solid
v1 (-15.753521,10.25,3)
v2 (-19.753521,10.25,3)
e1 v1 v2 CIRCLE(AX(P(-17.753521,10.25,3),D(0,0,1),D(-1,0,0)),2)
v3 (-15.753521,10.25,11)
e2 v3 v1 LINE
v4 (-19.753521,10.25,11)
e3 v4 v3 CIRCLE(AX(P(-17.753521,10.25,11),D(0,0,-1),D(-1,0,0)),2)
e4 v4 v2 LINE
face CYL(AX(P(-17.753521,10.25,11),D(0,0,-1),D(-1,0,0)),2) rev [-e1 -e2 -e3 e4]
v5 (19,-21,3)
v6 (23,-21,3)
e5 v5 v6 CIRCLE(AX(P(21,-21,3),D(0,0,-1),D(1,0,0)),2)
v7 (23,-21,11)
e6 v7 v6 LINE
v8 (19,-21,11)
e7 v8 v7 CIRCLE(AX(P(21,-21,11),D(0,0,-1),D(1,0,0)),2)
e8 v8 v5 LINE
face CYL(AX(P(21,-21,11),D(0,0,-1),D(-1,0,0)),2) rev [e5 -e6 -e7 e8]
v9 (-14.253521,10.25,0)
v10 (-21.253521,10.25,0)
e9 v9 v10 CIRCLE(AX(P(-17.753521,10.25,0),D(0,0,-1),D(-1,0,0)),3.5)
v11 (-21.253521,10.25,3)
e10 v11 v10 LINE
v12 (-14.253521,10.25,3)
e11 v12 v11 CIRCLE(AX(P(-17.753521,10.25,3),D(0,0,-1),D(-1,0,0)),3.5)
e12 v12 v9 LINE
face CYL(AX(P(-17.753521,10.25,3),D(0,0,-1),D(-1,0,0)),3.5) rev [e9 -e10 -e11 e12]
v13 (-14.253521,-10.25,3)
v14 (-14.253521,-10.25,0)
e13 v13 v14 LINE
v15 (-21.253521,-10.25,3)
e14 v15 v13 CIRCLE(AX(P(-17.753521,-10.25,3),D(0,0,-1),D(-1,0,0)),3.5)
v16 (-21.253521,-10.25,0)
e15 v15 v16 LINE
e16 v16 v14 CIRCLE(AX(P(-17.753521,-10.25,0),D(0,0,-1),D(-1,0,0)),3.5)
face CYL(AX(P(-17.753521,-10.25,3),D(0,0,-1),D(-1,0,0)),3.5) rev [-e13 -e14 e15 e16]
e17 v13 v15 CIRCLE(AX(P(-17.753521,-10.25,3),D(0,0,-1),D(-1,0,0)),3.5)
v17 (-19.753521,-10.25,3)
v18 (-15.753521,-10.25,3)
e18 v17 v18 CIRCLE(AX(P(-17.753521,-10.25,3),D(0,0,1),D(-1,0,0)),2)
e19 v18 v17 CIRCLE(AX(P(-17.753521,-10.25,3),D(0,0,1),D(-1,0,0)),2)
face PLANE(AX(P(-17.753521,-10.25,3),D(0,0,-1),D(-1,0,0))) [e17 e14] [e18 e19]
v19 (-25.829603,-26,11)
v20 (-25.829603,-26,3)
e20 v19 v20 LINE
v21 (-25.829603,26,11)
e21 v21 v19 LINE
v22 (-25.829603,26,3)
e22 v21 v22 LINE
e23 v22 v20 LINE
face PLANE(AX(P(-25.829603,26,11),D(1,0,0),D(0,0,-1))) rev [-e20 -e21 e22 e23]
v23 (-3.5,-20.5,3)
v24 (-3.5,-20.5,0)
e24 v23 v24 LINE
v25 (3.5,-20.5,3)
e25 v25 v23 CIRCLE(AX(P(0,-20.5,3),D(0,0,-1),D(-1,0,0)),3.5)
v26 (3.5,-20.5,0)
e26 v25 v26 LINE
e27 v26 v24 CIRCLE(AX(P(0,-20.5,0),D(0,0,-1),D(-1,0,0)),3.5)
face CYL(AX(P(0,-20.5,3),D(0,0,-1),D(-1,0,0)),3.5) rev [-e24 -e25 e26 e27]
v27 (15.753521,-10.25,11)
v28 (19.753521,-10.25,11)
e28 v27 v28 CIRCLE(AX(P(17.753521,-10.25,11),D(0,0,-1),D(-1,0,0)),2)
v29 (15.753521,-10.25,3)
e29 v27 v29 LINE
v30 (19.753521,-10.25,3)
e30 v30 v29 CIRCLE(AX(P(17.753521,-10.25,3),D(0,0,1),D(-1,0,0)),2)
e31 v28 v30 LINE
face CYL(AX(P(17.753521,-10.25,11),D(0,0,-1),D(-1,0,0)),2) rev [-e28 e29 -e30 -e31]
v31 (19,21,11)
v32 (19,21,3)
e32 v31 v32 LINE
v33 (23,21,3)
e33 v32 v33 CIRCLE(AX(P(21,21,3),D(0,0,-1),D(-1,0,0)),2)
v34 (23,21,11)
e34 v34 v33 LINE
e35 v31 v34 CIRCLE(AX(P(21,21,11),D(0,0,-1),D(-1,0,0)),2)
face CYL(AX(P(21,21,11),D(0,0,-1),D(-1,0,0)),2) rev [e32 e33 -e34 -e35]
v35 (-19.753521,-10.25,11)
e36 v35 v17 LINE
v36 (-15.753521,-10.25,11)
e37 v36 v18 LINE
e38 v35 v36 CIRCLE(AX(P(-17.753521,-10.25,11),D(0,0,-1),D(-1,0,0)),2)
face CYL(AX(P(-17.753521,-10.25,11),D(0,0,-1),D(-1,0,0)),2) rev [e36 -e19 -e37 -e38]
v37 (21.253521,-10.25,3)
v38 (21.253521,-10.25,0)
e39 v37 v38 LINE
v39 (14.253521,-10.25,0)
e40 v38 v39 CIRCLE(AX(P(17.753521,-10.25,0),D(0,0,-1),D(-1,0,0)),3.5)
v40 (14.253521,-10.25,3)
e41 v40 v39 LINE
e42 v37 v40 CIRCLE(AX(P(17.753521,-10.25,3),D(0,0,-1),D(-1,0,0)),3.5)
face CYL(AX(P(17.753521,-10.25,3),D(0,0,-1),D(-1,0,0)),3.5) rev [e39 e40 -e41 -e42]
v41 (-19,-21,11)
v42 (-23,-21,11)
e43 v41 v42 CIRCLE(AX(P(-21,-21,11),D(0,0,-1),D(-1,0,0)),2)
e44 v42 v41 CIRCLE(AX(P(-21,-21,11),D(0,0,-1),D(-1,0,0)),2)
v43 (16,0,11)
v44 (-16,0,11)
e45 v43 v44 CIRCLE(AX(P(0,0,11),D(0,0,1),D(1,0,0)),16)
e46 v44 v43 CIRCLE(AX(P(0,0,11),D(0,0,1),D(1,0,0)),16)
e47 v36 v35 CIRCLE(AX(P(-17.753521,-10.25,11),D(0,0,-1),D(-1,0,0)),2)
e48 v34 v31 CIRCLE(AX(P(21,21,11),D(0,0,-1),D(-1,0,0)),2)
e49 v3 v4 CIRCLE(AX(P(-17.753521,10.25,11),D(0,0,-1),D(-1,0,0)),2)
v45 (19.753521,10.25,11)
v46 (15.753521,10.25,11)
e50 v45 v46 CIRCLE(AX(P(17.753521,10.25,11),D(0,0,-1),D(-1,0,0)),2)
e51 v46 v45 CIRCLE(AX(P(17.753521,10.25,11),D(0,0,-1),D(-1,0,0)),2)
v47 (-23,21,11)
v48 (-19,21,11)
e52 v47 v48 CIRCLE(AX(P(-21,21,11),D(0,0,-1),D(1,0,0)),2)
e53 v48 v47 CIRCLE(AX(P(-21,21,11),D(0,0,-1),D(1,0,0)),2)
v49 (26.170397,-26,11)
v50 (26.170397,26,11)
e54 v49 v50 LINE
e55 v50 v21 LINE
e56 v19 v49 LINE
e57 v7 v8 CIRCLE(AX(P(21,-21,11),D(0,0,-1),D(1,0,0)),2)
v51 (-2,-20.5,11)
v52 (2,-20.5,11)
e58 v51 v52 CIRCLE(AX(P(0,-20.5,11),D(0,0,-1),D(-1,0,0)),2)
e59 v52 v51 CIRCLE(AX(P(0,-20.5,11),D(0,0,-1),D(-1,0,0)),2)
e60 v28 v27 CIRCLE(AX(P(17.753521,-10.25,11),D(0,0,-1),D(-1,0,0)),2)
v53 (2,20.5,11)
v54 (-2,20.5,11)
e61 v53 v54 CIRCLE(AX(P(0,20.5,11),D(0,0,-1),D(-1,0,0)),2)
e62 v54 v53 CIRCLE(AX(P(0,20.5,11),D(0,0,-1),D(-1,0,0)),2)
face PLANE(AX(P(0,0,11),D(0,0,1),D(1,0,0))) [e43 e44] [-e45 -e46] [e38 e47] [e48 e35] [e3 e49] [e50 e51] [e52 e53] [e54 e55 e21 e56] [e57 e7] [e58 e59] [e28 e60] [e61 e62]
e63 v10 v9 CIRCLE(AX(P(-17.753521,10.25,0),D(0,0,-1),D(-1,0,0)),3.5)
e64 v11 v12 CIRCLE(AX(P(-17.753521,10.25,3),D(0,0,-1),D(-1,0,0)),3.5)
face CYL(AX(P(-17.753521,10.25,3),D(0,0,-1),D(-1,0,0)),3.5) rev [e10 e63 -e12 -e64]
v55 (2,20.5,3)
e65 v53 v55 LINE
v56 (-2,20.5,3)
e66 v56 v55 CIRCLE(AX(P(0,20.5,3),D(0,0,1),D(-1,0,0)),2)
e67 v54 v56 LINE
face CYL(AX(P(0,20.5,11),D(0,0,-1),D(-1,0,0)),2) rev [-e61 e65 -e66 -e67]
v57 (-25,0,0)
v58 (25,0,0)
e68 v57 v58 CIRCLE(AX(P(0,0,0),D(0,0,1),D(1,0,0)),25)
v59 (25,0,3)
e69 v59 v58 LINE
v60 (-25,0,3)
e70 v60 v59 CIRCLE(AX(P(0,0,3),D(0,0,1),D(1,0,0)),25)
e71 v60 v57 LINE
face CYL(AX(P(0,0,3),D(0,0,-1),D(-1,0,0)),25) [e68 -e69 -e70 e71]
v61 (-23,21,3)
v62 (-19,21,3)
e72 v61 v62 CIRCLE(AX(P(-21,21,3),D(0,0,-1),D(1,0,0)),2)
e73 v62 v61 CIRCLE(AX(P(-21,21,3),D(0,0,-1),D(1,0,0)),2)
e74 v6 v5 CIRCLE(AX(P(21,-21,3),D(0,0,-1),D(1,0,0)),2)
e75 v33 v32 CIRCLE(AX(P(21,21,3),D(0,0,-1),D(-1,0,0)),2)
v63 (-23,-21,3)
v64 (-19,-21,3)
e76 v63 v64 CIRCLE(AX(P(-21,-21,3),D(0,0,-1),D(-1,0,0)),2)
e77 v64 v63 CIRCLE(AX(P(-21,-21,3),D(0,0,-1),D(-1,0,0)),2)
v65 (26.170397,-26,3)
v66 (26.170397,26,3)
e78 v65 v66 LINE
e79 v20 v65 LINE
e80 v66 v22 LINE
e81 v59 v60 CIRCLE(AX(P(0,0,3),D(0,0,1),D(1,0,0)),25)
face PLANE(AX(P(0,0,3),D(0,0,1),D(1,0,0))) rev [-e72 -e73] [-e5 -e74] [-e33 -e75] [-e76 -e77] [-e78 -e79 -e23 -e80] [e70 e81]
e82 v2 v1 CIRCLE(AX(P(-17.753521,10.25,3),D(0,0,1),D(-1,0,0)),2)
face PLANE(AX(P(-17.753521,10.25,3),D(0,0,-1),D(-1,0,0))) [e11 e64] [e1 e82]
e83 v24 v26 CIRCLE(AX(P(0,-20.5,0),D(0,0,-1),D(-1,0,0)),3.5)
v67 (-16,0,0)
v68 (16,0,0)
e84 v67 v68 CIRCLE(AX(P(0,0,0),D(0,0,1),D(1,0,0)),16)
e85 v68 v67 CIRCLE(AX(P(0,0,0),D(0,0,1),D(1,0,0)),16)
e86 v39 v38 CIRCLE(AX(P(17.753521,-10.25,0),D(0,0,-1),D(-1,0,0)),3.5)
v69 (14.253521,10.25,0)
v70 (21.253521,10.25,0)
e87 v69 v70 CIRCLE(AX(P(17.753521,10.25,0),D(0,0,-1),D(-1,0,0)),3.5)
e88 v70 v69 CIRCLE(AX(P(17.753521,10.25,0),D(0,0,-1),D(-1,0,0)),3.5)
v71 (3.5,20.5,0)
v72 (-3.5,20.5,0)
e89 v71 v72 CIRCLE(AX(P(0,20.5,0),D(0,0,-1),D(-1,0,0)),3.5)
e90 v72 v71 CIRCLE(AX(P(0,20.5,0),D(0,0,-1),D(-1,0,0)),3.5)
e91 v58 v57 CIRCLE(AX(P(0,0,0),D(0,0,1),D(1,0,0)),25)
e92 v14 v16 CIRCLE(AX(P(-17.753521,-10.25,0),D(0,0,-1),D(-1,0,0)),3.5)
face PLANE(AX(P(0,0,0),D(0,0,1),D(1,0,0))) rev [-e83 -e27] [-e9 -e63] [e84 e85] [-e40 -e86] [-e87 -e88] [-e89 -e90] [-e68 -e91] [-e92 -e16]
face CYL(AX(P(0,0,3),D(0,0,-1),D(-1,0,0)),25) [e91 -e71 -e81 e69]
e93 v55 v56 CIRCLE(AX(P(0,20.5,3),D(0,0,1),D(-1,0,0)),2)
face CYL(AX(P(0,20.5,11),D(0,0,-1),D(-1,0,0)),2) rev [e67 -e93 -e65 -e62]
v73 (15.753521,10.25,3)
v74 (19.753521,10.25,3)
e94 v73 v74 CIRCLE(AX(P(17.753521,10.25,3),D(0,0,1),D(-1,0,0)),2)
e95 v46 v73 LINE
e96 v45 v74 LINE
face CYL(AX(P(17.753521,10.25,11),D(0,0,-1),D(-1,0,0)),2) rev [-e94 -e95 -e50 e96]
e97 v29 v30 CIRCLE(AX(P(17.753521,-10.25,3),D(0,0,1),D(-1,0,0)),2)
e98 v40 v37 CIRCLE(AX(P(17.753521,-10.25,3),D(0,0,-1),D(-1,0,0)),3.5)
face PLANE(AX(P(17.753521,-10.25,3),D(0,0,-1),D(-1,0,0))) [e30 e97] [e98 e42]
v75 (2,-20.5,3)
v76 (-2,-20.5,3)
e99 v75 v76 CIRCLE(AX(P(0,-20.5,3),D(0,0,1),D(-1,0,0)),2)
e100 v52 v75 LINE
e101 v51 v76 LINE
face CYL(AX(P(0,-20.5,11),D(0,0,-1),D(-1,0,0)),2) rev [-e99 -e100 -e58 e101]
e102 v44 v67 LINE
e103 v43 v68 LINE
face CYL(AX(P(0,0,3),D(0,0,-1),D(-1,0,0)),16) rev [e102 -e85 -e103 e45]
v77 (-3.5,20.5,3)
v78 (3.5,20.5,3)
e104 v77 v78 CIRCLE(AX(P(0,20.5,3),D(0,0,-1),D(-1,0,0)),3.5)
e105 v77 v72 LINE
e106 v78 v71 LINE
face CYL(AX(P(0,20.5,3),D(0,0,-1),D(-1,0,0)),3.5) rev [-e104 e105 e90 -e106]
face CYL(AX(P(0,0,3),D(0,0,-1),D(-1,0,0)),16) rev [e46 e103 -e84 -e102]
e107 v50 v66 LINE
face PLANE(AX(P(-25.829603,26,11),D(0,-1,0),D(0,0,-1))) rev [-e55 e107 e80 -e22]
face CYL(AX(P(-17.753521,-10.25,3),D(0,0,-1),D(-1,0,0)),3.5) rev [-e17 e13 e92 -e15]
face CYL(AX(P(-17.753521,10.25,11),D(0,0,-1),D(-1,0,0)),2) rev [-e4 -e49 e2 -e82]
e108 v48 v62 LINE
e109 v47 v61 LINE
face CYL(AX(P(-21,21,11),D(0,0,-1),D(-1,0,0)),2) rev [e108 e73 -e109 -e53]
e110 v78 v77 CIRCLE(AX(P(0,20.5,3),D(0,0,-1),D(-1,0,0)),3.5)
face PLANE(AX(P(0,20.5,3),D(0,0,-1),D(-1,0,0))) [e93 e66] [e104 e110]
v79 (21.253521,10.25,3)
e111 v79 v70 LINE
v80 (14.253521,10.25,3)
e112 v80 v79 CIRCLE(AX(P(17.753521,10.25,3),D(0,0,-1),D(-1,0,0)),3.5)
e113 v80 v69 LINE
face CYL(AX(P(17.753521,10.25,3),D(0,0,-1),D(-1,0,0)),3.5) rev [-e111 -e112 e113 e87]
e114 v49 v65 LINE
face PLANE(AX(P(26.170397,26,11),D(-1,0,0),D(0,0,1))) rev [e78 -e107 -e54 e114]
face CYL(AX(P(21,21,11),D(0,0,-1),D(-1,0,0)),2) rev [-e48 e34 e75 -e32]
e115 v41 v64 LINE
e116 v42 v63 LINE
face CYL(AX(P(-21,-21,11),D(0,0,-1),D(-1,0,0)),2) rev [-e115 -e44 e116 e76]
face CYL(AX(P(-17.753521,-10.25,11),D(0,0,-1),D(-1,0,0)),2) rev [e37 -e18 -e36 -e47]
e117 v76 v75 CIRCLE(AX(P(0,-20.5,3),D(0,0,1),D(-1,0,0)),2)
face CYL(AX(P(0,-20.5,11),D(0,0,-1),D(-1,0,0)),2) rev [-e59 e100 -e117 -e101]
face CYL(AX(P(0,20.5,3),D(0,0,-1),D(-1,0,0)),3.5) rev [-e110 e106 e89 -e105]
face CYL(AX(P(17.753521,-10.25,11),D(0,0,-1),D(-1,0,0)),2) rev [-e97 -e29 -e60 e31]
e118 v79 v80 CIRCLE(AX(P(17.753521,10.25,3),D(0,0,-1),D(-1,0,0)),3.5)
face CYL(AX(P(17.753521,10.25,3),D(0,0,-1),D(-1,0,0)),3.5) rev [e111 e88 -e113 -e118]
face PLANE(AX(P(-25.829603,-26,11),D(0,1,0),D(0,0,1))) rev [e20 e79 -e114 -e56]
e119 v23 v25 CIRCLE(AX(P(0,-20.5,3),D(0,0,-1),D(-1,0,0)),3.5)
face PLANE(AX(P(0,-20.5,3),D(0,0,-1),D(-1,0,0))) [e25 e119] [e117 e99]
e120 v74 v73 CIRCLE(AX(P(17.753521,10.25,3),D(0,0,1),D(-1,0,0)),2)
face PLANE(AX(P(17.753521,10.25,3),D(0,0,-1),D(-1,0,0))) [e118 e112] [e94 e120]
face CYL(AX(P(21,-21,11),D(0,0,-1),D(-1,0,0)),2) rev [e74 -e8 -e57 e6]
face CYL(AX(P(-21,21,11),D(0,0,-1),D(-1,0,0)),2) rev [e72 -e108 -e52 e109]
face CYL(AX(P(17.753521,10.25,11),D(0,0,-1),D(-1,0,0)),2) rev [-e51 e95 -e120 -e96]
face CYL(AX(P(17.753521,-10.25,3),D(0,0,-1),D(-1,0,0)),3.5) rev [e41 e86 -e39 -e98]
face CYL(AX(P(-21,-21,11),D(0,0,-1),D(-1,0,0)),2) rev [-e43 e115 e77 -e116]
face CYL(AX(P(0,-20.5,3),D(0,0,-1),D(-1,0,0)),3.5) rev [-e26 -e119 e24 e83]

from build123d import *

# Parameters (mm, degrees)
SKETCH1_R           = 25
SKETCH1_R_2         = 16
BOSS_EXTRUDE1_DEPTH = 3
SKETCH2_W           = 52
SKETCH2_H           = 52
SKETCH2_R           = 16
BOSS_EXTRUDE2_DEPTH = 8
SKETCH3_R           = 2
CUT_EXTRUDE1_DEPTH  = 39.495320082
SKETCH4_R           = 2
CUT_EXTRUDE2_DEPTH  = 38.747710768
SKETCH5_R           = 3.5
CUT_EXTRUDE3_DEPTH  = 3


with BuildPart() as part:
    # Sketch1 → Boss-Extrude1 (new body)
    with BuildSketch(Plane.XY):
        Circle(SKETCH1_R)
        Circle(SKETCH1_R_2, mode=Mode.SUBTRACT)
    extrude(amount=BOSS_EXTRUDE1_DEPTH)

    # Sketch2 → Boss-Extrude2 (add)
    with BuildSketch(Plane.XY.offset(3)):
        with Locations((0.170396792, 0)):
            Rectangle(SKETCH2_W, SKETCH2_H)
        Circle(SKETCH2_R, mode=Mode.SUBTRACT)
    extrude(amount=BOSS_EXTRUDE2_DEPTH)

    # Sketch3 → Cut-Extrude1 (cut, through all)
    with BuildSketch(Plane(origin=(0, 0, 0), x_dir=(-1, 0, 0), z_dir=(0, 0, -1))):
        with Locations((0, 20.5)):
            Circle(SKETCH3_R)
        with Locations((17.753520778, 10.25)):
            Circle(SKETCH3_R)
        with Locations((17.753520778, -10.25)):
            Circle(SKETCH3_R)
        with Locations((0, -20.5)):
            Circle(SKETCH3_R)
        with Locations((-17.753520778, -10.25)):
            Circle(SKETCH3_R)
        with Locations((-17.753520778, 10.25)):
            Circle(SKETCH3_R)
    extrude(amount=-CUT_EXTRUDE1_DEPTH, mode=Mode.SUBTRACT)

    # Sketch4 → Cut-Extrude2 (cut, through all)
    with BuildSketch(Plane(origin=(0, 0, 3), x_dir=(-1, 0, 0), z_dir=(0, 0, -1))):
        with Locations((-21, 21)):
            Circle(SKETCH4_R)
        with Locations(Location((21, 21, 0), (0, 0, 180))):
            Circle(SKETCH4_R)
        with Locations((21, -21)):
            Circle(SKETCH4_R)
        with Locations(Location((-21, -21, 0), (0, 0, 180))):
            Circle(SKETCH4_R)
    extrude(amount=-CUT_EXTRUDE2_DEPTH, mode=Mode.SUBTRACT)

    # Sketch5 → Cut-Extrude3 (cut)
    with BuildSketch(Plane(origin=(0, 0, 0), x_dir=(-1, 0, 0), z_dir=(0, 0, -1))):
        with Locations((0, 20.5)):
            Circle(SKETCH5_R)
        with Locations((17.753520778, 10.25)):
            Circle(SKETCH5_R)
        with Locations((17.753520778, -10.25)):
            Circle(SKETCH5_R)
        with Locations((0, -20.5)):
            Circle(SKETCH5_R)
        with Locations((-17.753520778, -10.25)):
            Circle(SKETCH5_R)
        with Locations((-17.753520778, 10.25)):
            Circle(SKETCH5_R)
    extrude(amount=-CUT_EXTRUDE3_DEPTH, mode=Mode.SUBTRACT)


solid = part.part
